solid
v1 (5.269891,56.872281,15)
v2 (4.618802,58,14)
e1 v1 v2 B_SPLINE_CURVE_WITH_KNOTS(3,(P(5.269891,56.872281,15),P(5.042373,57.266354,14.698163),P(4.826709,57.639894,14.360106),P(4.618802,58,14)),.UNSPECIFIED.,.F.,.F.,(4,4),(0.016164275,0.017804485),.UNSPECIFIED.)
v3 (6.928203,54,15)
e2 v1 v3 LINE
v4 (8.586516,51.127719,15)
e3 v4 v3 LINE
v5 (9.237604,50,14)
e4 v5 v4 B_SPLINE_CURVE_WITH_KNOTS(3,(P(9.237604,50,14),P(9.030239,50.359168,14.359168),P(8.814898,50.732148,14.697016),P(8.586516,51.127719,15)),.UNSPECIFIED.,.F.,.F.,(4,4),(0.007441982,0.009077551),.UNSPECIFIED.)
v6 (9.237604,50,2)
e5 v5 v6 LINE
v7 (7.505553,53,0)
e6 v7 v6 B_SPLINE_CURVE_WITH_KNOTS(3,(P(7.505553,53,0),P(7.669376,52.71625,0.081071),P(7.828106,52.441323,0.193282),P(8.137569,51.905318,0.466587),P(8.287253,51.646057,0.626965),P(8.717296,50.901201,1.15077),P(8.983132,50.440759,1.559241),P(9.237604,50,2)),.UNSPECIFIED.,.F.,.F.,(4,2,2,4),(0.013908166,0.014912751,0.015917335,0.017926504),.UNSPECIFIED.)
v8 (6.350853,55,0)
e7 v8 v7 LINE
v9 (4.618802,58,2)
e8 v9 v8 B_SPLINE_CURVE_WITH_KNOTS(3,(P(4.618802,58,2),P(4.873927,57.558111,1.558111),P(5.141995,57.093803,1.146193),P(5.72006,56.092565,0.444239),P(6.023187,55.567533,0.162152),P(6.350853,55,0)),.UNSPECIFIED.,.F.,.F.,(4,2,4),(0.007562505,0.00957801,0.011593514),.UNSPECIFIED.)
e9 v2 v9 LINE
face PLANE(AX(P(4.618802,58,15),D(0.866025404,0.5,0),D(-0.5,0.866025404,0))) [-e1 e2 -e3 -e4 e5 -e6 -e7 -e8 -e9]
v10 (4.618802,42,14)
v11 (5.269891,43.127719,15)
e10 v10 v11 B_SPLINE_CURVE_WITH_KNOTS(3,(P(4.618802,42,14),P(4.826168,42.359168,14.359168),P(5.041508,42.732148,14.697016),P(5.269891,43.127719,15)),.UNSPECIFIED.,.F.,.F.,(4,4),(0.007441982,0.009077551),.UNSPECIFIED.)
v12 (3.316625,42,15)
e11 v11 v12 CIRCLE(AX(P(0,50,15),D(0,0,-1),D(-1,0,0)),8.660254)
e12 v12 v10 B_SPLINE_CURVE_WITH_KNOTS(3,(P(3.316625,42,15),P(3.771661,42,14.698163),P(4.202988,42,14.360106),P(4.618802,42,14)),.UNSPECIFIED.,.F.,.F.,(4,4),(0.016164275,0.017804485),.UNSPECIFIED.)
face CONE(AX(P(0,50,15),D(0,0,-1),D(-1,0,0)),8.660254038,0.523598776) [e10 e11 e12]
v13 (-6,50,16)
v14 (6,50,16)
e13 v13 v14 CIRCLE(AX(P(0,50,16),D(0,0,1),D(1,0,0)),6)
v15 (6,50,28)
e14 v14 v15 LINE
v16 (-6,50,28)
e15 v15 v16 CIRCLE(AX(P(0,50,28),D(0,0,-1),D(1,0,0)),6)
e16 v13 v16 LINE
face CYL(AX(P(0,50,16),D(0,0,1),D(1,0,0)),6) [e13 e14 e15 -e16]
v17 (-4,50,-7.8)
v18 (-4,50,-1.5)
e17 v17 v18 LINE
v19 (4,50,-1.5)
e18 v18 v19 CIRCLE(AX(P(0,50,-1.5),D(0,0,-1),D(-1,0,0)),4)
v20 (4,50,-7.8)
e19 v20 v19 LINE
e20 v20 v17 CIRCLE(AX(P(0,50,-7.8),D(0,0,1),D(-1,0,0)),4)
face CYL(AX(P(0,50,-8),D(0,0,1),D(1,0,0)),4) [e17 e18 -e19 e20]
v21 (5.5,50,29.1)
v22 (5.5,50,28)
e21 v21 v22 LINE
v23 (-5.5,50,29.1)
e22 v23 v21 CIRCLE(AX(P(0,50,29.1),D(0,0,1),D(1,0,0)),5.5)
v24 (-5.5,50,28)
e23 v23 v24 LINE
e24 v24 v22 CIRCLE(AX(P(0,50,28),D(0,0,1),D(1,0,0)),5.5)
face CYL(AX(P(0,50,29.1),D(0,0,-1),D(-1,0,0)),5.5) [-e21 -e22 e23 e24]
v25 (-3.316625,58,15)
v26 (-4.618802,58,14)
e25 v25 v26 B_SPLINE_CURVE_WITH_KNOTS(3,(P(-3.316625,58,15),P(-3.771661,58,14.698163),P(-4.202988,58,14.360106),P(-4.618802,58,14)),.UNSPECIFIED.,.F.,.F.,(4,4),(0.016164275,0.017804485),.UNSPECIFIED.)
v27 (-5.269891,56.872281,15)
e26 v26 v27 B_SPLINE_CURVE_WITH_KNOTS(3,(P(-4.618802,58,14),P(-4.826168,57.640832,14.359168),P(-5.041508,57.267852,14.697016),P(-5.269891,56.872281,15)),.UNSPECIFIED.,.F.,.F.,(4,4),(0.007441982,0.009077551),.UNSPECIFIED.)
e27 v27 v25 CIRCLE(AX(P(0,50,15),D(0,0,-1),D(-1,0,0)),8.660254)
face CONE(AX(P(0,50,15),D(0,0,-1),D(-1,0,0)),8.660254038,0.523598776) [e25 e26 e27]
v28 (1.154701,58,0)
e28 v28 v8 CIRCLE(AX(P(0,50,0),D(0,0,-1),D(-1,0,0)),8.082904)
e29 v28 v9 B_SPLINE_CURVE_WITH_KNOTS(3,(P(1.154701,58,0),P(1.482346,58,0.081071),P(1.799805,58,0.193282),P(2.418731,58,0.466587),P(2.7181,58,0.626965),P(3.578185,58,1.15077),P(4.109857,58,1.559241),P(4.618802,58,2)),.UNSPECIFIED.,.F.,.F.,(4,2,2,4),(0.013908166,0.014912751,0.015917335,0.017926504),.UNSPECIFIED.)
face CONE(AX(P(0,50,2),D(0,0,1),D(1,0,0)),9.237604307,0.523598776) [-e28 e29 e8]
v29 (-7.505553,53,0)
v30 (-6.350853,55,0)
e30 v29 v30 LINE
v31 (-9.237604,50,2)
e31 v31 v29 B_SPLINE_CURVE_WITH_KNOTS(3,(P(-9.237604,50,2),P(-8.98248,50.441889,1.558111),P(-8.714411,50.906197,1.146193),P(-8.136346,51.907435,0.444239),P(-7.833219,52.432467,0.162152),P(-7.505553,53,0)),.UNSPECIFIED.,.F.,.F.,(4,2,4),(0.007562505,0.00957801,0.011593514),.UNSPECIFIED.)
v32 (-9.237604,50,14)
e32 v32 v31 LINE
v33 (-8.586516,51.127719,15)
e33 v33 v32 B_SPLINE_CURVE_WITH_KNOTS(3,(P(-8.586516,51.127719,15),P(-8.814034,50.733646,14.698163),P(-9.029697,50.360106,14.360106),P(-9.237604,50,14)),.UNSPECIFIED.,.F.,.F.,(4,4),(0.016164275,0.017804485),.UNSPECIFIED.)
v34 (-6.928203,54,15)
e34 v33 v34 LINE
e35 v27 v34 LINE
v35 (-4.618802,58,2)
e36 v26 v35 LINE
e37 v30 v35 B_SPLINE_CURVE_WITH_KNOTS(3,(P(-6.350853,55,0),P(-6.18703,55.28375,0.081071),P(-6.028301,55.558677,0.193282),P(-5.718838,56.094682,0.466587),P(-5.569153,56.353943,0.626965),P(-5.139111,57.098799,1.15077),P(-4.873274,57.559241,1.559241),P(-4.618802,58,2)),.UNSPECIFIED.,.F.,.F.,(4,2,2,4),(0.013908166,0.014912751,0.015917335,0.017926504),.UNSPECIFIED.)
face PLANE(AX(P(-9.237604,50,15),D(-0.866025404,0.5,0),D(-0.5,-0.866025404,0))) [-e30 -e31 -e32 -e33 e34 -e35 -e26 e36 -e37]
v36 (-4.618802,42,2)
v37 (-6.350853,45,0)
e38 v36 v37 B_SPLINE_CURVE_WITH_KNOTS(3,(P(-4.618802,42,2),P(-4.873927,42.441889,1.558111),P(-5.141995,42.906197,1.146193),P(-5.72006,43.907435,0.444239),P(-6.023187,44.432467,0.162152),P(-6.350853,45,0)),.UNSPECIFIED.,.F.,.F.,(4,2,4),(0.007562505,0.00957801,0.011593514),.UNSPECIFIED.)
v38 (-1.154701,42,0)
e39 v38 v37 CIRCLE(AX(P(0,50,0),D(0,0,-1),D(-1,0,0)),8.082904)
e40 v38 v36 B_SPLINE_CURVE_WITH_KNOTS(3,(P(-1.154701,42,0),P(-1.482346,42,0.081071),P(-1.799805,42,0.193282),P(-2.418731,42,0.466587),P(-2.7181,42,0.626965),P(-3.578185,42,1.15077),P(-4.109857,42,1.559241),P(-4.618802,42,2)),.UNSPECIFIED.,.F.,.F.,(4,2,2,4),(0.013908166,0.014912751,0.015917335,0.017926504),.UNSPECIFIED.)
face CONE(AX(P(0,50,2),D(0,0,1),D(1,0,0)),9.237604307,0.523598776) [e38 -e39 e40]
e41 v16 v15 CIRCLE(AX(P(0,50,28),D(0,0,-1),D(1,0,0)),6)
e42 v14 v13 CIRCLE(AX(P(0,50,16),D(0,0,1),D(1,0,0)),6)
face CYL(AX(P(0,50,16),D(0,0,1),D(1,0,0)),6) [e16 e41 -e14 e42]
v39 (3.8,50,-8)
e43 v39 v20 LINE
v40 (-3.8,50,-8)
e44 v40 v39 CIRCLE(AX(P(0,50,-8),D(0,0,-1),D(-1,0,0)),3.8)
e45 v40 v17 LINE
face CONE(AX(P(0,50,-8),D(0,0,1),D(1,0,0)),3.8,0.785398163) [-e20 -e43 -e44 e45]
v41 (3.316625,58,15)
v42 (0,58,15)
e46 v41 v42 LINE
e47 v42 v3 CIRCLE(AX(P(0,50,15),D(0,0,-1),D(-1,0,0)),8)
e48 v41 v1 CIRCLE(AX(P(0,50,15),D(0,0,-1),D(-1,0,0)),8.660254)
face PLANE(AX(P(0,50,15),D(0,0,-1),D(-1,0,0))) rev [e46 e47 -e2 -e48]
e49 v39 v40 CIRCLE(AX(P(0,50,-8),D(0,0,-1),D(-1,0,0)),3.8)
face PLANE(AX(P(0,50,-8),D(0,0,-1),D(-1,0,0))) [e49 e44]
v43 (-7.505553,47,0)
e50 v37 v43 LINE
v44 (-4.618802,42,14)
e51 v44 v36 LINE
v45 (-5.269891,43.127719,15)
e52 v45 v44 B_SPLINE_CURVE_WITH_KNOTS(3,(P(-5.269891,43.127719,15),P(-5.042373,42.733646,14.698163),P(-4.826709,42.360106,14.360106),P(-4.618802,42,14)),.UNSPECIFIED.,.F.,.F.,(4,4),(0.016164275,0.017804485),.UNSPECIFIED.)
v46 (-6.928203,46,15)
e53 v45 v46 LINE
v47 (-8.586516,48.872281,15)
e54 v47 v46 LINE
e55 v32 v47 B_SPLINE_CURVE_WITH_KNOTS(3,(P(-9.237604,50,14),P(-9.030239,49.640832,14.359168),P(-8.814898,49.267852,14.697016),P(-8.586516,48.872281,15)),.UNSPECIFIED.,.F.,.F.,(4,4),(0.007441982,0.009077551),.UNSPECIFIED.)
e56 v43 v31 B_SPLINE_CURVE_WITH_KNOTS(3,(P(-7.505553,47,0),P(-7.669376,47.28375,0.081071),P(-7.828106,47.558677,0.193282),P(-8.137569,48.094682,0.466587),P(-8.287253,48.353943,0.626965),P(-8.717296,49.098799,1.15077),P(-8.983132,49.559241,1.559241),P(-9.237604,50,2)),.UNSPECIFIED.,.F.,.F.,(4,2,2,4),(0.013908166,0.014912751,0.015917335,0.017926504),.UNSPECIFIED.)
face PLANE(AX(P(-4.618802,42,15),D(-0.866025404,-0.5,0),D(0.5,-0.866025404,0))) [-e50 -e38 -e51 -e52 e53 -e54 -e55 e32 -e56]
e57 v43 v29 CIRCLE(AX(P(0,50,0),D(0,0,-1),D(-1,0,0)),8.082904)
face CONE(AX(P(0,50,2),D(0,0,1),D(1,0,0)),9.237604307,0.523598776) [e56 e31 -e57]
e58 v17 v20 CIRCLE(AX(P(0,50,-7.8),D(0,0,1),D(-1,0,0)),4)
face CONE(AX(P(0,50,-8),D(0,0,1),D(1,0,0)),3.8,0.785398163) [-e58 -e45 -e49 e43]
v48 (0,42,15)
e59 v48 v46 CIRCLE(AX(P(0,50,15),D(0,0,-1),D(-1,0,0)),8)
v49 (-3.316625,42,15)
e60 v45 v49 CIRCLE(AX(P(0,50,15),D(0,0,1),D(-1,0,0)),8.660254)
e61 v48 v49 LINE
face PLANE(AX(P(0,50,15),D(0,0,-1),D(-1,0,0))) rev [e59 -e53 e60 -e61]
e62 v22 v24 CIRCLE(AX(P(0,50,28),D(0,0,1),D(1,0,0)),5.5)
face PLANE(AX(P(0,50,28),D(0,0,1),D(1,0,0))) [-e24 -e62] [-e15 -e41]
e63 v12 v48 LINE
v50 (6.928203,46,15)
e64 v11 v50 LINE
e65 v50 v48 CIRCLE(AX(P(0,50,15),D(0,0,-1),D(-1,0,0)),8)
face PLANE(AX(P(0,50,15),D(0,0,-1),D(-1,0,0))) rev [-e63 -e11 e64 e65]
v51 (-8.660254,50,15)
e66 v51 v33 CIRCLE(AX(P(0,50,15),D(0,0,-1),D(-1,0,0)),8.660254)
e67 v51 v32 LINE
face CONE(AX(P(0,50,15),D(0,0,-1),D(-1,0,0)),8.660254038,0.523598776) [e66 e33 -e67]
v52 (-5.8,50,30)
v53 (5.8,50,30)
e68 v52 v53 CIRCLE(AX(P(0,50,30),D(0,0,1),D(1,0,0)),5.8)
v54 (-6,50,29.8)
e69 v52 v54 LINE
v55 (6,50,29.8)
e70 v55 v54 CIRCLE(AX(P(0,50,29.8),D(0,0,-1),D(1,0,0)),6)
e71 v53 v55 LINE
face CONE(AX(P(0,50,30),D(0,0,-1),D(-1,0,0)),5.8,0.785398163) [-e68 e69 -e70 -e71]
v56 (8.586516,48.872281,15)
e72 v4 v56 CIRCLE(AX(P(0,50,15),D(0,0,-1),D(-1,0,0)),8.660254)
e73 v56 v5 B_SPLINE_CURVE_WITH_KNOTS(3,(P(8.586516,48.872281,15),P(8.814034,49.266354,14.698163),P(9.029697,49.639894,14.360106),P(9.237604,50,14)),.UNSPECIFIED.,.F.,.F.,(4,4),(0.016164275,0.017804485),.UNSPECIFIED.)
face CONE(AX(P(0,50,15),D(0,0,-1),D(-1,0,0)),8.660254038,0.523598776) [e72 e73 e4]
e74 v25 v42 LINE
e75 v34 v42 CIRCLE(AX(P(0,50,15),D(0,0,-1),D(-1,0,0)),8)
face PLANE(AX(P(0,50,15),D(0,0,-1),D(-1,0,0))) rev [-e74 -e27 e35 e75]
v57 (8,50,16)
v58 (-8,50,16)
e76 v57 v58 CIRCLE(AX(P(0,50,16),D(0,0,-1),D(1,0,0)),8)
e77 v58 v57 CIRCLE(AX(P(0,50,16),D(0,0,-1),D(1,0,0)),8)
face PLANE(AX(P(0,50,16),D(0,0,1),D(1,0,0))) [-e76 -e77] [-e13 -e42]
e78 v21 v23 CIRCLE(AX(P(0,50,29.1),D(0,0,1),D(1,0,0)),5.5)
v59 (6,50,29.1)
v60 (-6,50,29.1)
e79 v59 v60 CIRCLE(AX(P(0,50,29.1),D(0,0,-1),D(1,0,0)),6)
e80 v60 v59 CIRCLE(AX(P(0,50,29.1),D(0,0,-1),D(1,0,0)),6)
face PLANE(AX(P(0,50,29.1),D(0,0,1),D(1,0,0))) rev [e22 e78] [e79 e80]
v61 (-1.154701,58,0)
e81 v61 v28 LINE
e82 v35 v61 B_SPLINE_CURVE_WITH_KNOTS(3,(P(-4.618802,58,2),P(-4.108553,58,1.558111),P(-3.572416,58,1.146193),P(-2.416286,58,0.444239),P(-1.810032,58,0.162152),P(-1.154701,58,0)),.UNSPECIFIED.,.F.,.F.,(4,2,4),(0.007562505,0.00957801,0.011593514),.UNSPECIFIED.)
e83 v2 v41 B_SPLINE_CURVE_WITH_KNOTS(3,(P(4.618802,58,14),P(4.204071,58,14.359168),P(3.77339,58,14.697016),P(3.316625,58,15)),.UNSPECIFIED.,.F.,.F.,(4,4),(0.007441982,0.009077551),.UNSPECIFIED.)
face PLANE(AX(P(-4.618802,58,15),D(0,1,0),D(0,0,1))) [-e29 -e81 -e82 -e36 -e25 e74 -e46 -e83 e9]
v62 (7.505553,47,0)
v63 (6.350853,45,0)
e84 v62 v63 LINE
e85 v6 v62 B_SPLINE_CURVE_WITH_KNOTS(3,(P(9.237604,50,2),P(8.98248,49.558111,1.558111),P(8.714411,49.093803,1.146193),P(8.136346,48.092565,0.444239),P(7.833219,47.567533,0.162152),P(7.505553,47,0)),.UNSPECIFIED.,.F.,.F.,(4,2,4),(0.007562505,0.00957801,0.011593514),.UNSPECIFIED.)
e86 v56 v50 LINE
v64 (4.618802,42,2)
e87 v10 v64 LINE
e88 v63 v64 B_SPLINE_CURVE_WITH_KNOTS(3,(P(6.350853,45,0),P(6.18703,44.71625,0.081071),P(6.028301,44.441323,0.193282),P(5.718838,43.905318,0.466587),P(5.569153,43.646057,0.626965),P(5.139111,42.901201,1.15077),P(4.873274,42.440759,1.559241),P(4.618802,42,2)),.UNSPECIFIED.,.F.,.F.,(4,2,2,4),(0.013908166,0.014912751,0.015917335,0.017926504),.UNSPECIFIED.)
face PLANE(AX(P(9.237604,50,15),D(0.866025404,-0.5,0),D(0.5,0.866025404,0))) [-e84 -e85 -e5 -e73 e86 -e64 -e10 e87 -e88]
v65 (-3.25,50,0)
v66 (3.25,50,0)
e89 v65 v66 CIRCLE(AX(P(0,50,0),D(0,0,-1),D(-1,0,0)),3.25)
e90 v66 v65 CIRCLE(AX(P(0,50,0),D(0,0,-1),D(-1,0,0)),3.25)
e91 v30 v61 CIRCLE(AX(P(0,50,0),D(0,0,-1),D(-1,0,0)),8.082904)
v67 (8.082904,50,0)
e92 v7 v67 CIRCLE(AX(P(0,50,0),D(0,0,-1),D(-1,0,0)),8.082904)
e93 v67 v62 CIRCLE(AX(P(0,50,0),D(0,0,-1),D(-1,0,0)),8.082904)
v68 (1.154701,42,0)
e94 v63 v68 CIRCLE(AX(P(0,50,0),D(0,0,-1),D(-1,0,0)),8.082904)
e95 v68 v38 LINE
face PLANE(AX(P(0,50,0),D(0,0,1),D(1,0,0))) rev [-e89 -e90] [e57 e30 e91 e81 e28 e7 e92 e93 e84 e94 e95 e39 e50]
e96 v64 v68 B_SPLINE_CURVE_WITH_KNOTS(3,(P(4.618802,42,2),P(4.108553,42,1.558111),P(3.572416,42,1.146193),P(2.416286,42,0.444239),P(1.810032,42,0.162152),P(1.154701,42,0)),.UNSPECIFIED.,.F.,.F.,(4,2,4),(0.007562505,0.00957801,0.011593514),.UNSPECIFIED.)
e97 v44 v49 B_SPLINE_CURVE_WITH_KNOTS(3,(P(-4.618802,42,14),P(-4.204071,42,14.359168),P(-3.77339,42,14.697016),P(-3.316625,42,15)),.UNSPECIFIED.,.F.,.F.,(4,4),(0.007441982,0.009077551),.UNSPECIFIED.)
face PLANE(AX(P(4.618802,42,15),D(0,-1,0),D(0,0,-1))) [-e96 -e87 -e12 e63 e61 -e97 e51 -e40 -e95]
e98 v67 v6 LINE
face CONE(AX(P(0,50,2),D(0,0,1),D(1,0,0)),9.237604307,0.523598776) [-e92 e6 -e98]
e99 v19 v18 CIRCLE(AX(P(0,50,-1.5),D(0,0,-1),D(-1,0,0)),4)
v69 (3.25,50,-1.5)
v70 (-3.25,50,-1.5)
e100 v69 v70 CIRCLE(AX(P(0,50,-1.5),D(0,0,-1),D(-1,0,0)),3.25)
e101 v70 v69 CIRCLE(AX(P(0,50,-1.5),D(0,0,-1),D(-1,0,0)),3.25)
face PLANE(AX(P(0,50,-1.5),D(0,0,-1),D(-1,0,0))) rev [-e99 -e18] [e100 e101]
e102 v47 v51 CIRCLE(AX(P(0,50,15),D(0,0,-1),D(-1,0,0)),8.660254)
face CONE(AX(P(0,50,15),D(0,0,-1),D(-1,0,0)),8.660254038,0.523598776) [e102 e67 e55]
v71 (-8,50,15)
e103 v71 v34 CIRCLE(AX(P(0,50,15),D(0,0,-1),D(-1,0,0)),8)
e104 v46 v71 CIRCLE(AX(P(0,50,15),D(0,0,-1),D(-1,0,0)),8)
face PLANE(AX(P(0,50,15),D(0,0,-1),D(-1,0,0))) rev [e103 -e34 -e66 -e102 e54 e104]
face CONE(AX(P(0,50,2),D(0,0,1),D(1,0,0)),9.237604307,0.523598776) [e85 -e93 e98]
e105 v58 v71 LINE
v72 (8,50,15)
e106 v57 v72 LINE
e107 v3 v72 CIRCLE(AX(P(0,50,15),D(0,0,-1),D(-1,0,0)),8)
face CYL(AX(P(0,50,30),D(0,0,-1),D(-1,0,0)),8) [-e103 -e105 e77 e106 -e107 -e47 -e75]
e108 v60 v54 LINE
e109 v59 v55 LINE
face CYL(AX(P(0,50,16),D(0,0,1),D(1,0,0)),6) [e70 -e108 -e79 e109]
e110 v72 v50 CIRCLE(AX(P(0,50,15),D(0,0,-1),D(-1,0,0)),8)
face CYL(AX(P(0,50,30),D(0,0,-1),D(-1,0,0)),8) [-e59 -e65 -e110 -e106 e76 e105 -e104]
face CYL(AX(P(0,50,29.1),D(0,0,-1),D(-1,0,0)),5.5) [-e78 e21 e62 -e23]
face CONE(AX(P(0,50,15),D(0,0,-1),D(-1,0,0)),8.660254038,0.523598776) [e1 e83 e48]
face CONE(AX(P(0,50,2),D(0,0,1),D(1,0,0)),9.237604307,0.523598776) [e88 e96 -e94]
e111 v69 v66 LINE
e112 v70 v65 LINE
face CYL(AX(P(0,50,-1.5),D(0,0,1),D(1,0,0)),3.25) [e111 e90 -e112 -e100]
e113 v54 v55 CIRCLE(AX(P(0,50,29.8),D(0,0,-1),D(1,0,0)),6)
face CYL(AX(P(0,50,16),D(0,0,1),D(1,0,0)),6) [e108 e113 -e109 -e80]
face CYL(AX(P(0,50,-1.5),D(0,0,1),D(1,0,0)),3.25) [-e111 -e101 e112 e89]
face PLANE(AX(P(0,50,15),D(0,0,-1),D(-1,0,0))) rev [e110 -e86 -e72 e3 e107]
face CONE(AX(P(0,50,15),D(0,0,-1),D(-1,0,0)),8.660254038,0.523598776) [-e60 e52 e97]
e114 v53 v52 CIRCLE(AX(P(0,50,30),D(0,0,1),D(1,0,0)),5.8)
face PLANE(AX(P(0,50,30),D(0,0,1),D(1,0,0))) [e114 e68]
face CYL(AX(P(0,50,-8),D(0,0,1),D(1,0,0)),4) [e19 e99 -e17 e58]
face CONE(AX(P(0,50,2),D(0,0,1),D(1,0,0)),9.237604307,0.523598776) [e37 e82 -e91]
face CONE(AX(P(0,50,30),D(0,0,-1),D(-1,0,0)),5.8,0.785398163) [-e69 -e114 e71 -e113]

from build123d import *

# Parameters (mm, degrees)
SKETCH1_R           = 12.5
BOSS_EXTRUDE1_DEPTH = 30
SKETCH2_OUTSIDE_W   = 36.274
SKETCH2_OUTSIDE_H   = 36.274
CUT_EXTRUDE1_DEPTH  = 15
SKETCH3_OUTSIDE_W   = 36.274
SKETCH3_OUTSIDE_H   = 36.274
SKETCH3_OUTSIDE_R   = 8
CUT_EXTRUDE2_DEPTH  = 66.479004269
SKETCH4_R           = 4
BOSS_EXTRUDE2_DEPTH = 8
SKETCH5_OUTSIDE_W   = 29.512
SKETCH5_OUTSIDE_H   = 27.036
SKETCH5_OUTSIDE_R   = 3.25
CUT_EXTRUDE3_DEPTH  = 1.5
SKETCH6_OUTSIDE_W   = 29.512
SKETCH6_OUTSIDE_H   = 27.036
SKETCH6_OUTSIDE_R   = 6
CUT_EXTRUDE4_DEPTH  = 14
SKETCH8_OUTSIDE_W   = 29.512
SKETCH8_OUTSIDE_H   = 27.036
SKETCH8_OUTSIDE_R   = 5.5
CUT_EXTRUDE5_DEPTH  = 1.1
CHAMFER1_SIZE       = 0.2


with BuildPart() as part:
    # Sketch1 → Boss-Extrude1 (new body)
    with BuildSketch(Plane.XY):
        with Locations((0, 50)):
            Circle(SKETCH1_R)
    extrude(amount=BOSS_EXTRUDE1_DEPTH)

    # Sketch2 outside → Cut-Extrude1 (cut)
    with BuildSketch(Plane(origin=(0, 0, 0), x_dir=(-1, 0, 0), z_dir=(0, 0, -1))):
        with Locations((0, 50)):
            Rectangle(SKETCH2_OUTSIDE_W, SKETCH2_OUTSIDE_H)
        Polygon((-4.618802154, 42), (4.618802154, 42), (9.237604307, 50), (4.618802154, 58), (-4.618802154, 58), (-9.237604307, 50), align=None, mode=Mode.SUBTRACT)
    extrude(amount=-CUT_EXTRUDE1_DEPTH, mode=Mode.SUBTRACT)

    # Sketch3 outside → Cut-Extrude2 (cut, through all)
    with BuildSketch(Plane(origin=(0, 0, 15), x_dir=(-1, 0, 0), z_dir=(0, 0, -1))):
        with Locations((0, 50)):
            Rectangle(SKETCH3_OUTSIDE_W, SKETCH3_OUTSIDE_H)
        with Locations((0, 50)):
            Circle(SKETCH3_OUTSIDE_R, mode=Mode.SUBTRACT)
    extrude(amount=-CUT_EXTRUDE2_DEPTH, mode=Mode.SUBTRACT)

    # Sketch4 → Boss-Extrude2 (add)
    with BuildSketch(Plane(origin=(0, 0, 0), x_dir=(-1, 0, 0), z_dir=(0, 0, -1))):
        with Locations(Location((0, 50, 0), (0, 0, 180))):
            Circle(SKETCH4_R)
    extrude(amount=BOSS_EXTRUDE2_DEPTH)

    # Sketch5 outside → Cut-Extrude3 (cut)
    with BuildSketch(Plane(origin=(0, 0, 0), x_dir=(-1, 0, 0), z_dir=(0, 0, -1))):
        with Locations((0, 50)):
            Rectangle(SKETCH5_OUTSIDE_W, SKETCH5_OUTSIDE_H)
        with Locations((0, 50)):
            Circle(SKETCH5_OUTSIDE_R, mode=Mode.SUBTRACT)
    extrude(amount=CUT_EXTRUDE3_DEPTH, mode=Mode.SUBTRACT)

    # Sketch6 outside → Cut-Extrude4 (cut)
    with BuildSketch(Plane.XY.offset(30)):
        with Locations((0, 50)):
            Rectangle(SKETCH6_OUTSIDE_W, SKETCH6_OUTSIDE_H)
        with Locations((0, 50)):
            Circle(SKETCH6_OUTSIDE_R, mode=Mode.SUBTRACT)
    extrude(amount=-CUT_EXTRUDE4_DEPTH, mode=Mode.SUBTRACT)

    # Sketch8 outside → Cut-Extrude5 (cut)
    with BuildSketch(Plane.XY.offset(28)):
        with Locations((0, 50)):
            Rectangle(SKETCH8_OUTSIDE_W, SKETCH8_OUTSIDE_H)
        with Locations((0, 50)):
            Circle(SKETCH8_OUTSIDE_R, mode=Mode.SUBTRACT)
    extrude(amount=CUT_EXTRUDE5_DEPTH, mode=Mode.SUBTRACT)

    # Chamfer1
    chamfer1_edges = [part.edges().sort_by_distance(p)[0] for p in [
        (-4, 50, -8),
        (-6, 50, 30),
    ]]
    chamfer(chamfer1_edges, length=CHAMFER1_SIZE)

    # Sketch10 → Cut-Revolve1 (revolve, cut)
    with BuildSketch(Plane(origin=(0, 50, 0), x_dir=(1, 0, 0), z_dir=(0, 1, 0))):
        Polygon((-9.237604307, 0), (-9.237604307, -2), (-8.082903769, 0), align=None)
        Polygon((-9.237604307, -15), (-9.237604307, -14), (-8.660254038, -15), align=None)
    revolve(axis=Axis((0, 50, -8), (0, 0, 1)), mode=Mode.SUBTRACT)


solid = part.part
